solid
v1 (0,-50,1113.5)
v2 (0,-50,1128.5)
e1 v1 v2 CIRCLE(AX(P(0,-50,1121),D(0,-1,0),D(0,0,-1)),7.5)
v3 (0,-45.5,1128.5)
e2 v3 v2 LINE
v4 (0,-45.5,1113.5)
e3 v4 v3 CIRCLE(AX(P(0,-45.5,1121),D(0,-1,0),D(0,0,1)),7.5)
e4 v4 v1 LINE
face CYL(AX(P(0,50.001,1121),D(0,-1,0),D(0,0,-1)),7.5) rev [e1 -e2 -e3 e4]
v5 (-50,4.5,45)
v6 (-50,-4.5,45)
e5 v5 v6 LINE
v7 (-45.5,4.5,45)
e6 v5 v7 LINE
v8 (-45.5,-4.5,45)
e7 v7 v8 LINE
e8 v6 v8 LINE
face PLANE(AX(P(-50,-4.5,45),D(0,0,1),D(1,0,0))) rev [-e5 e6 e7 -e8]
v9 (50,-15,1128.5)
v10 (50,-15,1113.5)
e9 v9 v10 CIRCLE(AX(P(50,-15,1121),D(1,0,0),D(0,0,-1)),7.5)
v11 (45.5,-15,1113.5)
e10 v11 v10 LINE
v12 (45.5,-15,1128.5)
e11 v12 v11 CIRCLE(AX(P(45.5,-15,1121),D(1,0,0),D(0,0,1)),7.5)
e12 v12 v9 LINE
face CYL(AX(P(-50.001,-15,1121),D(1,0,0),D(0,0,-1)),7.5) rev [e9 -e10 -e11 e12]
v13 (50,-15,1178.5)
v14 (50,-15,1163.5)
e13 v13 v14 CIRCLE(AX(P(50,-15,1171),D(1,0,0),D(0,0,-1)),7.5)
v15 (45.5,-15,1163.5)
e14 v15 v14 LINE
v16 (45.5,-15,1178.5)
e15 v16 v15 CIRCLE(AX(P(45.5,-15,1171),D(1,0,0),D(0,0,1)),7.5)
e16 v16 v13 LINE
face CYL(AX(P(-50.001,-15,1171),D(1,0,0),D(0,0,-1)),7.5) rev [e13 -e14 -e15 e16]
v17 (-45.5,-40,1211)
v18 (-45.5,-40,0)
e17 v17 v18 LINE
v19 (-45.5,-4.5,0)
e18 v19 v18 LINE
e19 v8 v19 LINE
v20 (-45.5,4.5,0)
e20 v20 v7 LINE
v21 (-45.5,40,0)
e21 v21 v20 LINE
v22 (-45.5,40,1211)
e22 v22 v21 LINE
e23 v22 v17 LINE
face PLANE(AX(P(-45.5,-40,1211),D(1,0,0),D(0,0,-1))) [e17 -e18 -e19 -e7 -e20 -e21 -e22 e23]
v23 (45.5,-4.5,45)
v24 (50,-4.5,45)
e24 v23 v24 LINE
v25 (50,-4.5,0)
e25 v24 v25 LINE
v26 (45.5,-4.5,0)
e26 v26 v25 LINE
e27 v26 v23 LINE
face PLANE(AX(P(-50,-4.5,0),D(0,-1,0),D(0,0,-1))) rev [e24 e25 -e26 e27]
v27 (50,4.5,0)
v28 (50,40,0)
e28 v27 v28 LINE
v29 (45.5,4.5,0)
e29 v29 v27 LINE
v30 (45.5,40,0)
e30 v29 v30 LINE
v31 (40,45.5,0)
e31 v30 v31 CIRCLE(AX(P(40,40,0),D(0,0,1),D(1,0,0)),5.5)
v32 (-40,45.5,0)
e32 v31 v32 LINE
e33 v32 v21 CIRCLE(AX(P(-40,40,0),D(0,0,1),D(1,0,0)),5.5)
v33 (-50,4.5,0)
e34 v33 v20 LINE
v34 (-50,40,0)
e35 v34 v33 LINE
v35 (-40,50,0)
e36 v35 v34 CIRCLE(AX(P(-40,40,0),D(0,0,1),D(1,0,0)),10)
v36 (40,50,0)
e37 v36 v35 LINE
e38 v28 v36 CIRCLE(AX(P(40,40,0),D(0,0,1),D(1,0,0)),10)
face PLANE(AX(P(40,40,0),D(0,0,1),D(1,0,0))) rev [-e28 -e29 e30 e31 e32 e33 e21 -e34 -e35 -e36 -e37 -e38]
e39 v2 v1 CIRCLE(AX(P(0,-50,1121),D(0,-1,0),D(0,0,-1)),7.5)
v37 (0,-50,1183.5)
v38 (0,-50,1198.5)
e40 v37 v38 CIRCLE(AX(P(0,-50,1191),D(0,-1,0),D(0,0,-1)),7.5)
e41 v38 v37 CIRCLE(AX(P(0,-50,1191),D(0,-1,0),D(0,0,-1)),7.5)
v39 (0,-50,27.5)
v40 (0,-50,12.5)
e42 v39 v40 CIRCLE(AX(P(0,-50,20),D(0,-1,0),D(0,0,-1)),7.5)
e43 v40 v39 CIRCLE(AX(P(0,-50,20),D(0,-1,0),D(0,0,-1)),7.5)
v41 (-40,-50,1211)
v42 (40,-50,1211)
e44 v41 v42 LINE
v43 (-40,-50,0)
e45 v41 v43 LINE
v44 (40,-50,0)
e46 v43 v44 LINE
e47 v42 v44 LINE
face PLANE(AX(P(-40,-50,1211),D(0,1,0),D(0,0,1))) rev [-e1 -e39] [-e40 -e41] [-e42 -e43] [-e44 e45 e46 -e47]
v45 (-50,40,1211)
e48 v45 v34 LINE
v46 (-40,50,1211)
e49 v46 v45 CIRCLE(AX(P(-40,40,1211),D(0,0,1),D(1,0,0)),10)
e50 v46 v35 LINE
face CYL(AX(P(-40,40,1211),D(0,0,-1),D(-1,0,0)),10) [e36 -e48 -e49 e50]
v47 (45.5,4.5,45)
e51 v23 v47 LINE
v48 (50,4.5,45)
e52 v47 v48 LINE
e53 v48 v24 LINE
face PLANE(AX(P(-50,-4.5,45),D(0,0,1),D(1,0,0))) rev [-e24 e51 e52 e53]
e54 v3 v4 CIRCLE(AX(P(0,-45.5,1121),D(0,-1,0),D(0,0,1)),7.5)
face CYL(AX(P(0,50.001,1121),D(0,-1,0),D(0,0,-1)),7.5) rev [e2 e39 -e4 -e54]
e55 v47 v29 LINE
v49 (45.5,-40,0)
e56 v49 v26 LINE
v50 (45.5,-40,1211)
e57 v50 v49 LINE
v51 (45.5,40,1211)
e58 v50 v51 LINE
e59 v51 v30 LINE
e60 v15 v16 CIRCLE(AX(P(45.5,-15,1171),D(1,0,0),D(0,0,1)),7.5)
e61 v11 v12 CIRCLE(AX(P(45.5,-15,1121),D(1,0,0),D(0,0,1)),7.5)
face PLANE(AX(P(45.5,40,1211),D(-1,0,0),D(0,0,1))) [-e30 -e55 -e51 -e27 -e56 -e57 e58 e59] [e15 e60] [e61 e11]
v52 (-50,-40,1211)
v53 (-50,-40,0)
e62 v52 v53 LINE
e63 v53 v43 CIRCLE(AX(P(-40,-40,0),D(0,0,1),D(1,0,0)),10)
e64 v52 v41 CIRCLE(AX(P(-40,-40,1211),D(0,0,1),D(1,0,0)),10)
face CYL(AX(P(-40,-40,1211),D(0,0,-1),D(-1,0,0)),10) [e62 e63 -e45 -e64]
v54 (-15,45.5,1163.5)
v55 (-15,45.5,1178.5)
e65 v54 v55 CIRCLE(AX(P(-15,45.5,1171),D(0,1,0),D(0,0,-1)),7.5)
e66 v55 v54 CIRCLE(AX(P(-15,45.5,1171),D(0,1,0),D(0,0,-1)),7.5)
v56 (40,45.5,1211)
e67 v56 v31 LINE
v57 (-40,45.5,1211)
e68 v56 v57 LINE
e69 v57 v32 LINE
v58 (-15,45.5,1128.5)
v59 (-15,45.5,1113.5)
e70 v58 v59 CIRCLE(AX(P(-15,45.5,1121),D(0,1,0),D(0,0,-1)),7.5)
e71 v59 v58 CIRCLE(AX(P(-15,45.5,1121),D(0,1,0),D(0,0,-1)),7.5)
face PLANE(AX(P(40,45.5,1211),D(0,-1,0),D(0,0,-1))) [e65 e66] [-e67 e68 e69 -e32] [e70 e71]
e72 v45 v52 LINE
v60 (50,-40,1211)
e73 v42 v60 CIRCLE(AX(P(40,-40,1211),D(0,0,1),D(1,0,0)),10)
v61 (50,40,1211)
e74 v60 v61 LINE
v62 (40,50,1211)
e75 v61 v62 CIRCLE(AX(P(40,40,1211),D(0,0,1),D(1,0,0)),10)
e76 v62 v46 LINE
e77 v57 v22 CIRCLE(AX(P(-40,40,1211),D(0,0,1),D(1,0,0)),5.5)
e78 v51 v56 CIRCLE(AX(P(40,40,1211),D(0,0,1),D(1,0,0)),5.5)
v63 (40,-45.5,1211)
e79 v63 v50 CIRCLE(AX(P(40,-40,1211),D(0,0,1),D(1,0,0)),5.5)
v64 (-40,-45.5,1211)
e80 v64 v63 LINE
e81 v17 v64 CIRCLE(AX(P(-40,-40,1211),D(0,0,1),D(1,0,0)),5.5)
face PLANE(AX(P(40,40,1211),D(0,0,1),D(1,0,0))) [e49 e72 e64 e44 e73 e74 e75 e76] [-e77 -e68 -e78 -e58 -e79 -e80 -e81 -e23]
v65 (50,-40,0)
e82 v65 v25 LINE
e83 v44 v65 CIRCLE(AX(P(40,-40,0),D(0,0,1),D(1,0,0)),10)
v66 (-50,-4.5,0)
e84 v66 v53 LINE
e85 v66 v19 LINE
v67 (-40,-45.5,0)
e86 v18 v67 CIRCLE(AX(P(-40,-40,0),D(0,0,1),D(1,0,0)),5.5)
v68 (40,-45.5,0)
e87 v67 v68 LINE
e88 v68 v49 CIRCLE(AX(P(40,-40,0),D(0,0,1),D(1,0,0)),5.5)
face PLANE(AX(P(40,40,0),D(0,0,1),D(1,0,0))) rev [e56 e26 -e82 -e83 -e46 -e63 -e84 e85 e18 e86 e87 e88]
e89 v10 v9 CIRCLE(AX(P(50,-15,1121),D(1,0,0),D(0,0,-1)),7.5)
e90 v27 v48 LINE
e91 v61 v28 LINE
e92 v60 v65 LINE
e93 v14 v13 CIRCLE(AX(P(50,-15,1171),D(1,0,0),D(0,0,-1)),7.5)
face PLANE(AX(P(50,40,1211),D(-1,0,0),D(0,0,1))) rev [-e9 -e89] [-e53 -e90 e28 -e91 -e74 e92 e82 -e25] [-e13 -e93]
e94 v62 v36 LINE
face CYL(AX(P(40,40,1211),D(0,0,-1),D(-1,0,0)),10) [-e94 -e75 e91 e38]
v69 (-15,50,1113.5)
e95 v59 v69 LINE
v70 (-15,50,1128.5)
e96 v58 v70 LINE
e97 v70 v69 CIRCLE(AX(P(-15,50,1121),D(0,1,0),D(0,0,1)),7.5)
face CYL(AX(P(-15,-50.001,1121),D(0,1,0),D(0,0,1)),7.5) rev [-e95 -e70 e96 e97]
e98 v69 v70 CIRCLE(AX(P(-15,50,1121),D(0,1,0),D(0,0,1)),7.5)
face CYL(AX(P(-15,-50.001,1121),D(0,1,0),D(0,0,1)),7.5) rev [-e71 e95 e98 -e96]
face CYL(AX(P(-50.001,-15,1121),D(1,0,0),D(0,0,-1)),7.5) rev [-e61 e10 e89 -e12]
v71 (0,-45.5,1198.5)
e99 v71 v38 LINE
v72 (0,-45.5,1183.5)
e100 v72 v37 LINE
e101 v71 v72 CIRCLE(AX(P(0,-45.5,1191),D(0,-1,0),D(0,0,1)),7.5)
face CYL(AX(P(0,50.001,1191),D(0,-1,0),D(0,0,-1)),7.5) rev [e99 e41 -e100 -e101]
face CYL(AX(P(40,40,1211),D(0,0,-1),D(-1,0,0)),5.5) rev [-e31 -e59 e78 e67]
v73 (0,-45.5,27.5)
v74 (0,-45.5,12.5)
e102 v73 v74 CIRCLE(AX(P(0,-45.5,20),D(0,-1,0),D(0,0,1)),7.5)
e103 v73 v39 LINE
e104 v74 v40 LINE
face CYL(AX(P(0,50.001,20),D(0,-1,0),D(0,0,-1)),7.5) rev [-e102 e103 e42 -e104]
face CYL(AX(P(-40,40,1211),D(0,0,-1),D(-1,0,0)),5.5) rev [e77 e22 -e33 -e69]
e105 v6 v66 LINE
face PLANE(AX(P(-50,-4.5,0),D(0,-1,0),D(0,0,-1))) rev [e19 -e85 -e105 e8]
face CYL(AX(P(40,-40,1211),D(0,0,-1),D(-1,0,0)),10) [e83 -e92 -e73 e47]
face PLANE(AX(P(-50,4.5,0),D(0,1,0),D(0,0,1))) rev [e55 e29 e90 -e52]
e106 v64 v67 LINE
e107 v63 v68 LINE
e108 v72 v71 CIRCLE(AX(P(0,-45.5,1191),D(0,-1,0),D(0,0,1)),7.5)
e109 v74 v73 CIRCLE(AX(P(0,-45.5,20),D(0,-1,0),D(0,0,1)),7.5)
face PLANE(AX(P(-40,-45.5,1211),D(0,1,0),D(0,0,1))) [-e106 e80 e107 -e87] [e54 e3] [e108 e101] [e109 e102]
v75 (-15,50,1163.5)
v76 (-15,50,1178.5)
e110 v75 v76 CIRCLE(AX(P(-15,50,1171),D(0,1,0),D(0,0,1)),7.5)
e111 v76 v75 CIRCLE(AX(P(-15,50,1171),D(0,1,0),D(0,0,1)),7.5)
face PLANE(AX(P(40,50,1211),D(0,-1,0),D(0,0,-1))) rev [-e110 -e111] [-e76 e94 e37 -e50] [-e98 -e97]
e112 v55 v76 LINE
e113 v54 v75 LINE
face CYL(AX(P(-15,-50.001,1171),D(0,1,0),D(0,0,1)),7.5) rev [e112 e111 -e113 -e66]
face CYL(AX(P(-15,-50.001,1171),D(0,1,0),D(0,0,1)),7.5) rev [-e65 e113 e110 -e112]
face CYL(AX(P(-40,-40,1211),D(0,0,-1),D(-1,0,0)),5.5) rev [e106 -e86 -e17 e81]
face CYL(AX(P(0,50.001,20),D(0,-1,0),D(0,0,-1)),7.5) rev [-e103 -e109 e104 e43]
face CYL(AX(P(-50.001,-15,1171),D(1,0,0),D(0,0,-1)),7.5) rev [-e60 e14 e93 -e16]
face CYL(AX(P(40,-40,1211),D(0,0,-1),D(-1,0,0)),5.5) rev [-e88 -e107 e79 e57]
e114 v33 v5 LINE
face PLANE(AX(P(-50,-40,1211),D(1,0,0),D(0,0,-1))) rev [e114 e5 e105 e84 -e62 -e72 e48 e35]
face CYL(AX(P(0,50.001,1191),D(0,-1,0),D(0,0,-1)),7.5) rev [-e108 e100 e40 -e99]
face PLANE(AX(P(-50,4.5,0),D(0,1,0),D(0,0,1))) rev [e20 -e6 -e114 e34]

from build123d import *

# Parameters (mm, degrees)
BOSS_EXTRUDE1_DEPTH = 1211
CUT_EXTRUDE1_REACH  = 1218.15
SKETCH_1_R          = 7.5
CUT_EXTRUDE2_REACH  = 1218.15
SKETCH2_R           = 7.5
CUT_EXTRUDE3_REACH  = 1218.15
SKETCH3_R           = 7.5
SKETCH4_W           = 45
SKETCH4_H           = 9
CUT_EXTRUDE4_DEPTH  = 1217.150072976


with BuildPart() as part:
    # Sketch1 → Boss-Extrude1 (new body)
    with BuildSketch(Plane.XY):
        with BuildLine():
            Line((-40, -50), (40, -50))
            ThreePointArc((40, -50), (47.071067812, -47.071067812), (50, -40))
            Line((50, -40), (50, 40))
            ThreePointArc((50, 40), (47.071067812, 47.071067812), (40, 50))
            Line((40, 50), (-40, 50))
            ThreePointArc((-40, 50), (-47.071067812, 47.071067812), (-50, 40))
            Line((-50, 40), (-50, -40))
            ThreePointArc((-50, -40), (-47.071067812, -47.071067812), (-40, -50))
        make_face()
        with BuildLine():
            Line((-40, -45.5), (40, -45.5))
            ThreePointArc((40, -45.5), (43.889087297, -43.889087297), (45.5, -40))
            Line((45.5, -40), (45.5, 40))
            ThreePointArc((45.5, 40), (43.889087297, 43.889087297), (40, 45.5))
            Line((40, 45.5), (-40, 45.5))
            ThreePointArc((-40, 45.5), (-43.889087297, 43.889087297), (-45.5, 40))
            Line((-45.5, 40), (-45.5, -40))
            ThreePointArc((-45.5, -40), (-43.889087297, -43.889087297), (-40, -45.5))
        make_face(mode=Mode.SUBTRACT)
    extrude(amount=BOSS_EXTRUDE1_DEPTH)

    # 草图1 → Cut-Extrude1 (cut, up to next)
    with BuildSketch(Plane(origin=(50, 0, 0), x_dir=(0, 0, -1), z_dir=(1, 0, 0)), mode=Mode.PRIVATE) as cut_extrude1_sk1:
        with Locations((-1171, -15)):
            Circle(SKETCH_1_R)
    cut_extrude1_tool1 = extrude(cut_extrude1_sk1.sketch, amount=-CUT_EXTRUDE1_REACH, mode=Mode.PRIVATE) & part.part
    # 草图1 → Cut-Extrude1 (cut, up to next)
    with BuildSketch(Plane(origin=(50, 0, 0), x_dir=(0, 0, -1), z_dir=(1, 0, 0)), mode=Mode.PRIVATE) as cut_extrude1_sk2:
        with Locations((-1121, -15)):
            Circle(SKETCH_1_R)
    cut_extrude1_tool2 = extrude(cut_extrude1_sk2.sketch, amount=-CUT_EXTRUDE1_REACH, mode=Mode.PRIVATE) & part.part
    add(cut_extrude1_tool1.solids().sort_by_distance((50, -15, 1171))[0], mode=Mode.SUBTRACT)
    add(cut_extrude1_tool2.solids().sort_by_distance((50, -15, 1121))[0], mode=Mode.SUBTRACT)

    # Sketch2 → Cut-Extrude2 (cut, up to next)
    with BuildSketch(Plane.XZ.offset(50), mode=Mode.PRIVATE) as cut_extrude2_sk1:
        with Locations(Location((0, 1191, 0), (0, 0, 270))):
            Circle(SKETCH2_R)
    cut_extrude2_tool1 = extrude(cut_extrude2_sk1.sketch, amount=-CUT_EXTRUDE2_REACH, mode=Mode.PRIVATE) & part.part
    # Sketch2 → Cut-Extrude2 (cut, up to next)
    with BuildSketch(Plane.XZ.offset(50), mode=Mode.PRIVATE) as cut_extrude2_sk2:
        with Locations(Location((0, 1121, 0), (0, 0, 270))):
            Circle(SKETCH2_R)
    cut_extrude2_tool2 = extrude(cut_extrude2_sk2.sketch, amount=-CUT_EXTRUDE2_REACH, mode=Mode.PRIVATE) & part.part
    # Sketch2 → Cut-Extrude2 (cut, up to next)
    with BuildSketch(Plane.XZ.offset(50), mode=Mode.PRIVATE) as cut_extrude2_sk3:
        with Locations(Location((0, 20, 0), (0, 0, 270))):
            Circle(SKETCH2_R)
    cut_extrude2_tool3 = extrude(cut_extrude2_sk3.sketch, amount=-CUT_EXTRUDE2_REACH, mode=Mode.PRIVATE) & part.part
    add(cut_extrude2_tool1.solids().sort_by_distance((0, -50, 1191))[0], mode=Mode.SUBTRACT)
    add(cut_extrude2_tool2.solids().sort_by_distance((0, -50, 1121))[0], mode=Mode.SUBTRACT)
    add(cut_extrude2_tool3.solids().sort_by_distance((0, -50, 20))[0], mode=Mode.SUBTRACT)

    # Sketch3 → Cut-Extrude3 (cut, up to next)
    with BuildSketch(Plane(origin=(0, 50, 0), x_dir=(1, 0, 0), z_dir=(0, 1, 0)), mode=Mode.PRIVATE) as cut_extrude3_sk1:
        with Locations(Location((-15, -1171, 0), (0, 0, 270))):
            Circle(SKETCH3_R)
    cut_extrude3_tool1 = extrude(cut_extrude3_sk1.sketch, amount=-CUT_EXTRUDE3_REACH, mode=Mode.PRIVATE) & part.part
    # Sketch3 → Cut-Extrude3 (cut, up to next)
    with BuildSketch(Plane(origin=(0, 50, 0), x_dir=(1, 0, 0), z_dir=(0, 1, 0)), mode=Mode.PRIVATE) as cut_extrude3_sk2:
        with Locations(Location((-15, -1121, 0), (0, 0, 270))):
            Circle(SKETCH3_R)
    cut_extrude3_tool2 = extrude(cut_extrude3_sk2.sketch, amount=-CUT_EXTRUDE3_REACH, mode=Mode.PRIVATE) & part.part
    add(cut_extrude3_tool1.solids().sort_by_distance((-15, 50, 1171))[0], mode=Mode.SUBTRACT)
    add(cut_extrude3_tool2.solids().sort_by_distance((-15, 50, 1121))[0], mode=Mode.SUBTRACT)

    # Sketch4 → Cut-Extrude4 (cut, through all)
    with BuildSketch(Plane(origin=(50, 0, 0), x_dir=(0, 0, -1), z_dir=(1, 0, 0))):
        with Locations((-22.5, 0)):
            Rectangle(SKETCH4_W, SKETCH4_H)
    extrude(amount=-CUT_EXTRUDE4_DEPTH, mode=Mode.SUBTRACT)


solid = part.part
